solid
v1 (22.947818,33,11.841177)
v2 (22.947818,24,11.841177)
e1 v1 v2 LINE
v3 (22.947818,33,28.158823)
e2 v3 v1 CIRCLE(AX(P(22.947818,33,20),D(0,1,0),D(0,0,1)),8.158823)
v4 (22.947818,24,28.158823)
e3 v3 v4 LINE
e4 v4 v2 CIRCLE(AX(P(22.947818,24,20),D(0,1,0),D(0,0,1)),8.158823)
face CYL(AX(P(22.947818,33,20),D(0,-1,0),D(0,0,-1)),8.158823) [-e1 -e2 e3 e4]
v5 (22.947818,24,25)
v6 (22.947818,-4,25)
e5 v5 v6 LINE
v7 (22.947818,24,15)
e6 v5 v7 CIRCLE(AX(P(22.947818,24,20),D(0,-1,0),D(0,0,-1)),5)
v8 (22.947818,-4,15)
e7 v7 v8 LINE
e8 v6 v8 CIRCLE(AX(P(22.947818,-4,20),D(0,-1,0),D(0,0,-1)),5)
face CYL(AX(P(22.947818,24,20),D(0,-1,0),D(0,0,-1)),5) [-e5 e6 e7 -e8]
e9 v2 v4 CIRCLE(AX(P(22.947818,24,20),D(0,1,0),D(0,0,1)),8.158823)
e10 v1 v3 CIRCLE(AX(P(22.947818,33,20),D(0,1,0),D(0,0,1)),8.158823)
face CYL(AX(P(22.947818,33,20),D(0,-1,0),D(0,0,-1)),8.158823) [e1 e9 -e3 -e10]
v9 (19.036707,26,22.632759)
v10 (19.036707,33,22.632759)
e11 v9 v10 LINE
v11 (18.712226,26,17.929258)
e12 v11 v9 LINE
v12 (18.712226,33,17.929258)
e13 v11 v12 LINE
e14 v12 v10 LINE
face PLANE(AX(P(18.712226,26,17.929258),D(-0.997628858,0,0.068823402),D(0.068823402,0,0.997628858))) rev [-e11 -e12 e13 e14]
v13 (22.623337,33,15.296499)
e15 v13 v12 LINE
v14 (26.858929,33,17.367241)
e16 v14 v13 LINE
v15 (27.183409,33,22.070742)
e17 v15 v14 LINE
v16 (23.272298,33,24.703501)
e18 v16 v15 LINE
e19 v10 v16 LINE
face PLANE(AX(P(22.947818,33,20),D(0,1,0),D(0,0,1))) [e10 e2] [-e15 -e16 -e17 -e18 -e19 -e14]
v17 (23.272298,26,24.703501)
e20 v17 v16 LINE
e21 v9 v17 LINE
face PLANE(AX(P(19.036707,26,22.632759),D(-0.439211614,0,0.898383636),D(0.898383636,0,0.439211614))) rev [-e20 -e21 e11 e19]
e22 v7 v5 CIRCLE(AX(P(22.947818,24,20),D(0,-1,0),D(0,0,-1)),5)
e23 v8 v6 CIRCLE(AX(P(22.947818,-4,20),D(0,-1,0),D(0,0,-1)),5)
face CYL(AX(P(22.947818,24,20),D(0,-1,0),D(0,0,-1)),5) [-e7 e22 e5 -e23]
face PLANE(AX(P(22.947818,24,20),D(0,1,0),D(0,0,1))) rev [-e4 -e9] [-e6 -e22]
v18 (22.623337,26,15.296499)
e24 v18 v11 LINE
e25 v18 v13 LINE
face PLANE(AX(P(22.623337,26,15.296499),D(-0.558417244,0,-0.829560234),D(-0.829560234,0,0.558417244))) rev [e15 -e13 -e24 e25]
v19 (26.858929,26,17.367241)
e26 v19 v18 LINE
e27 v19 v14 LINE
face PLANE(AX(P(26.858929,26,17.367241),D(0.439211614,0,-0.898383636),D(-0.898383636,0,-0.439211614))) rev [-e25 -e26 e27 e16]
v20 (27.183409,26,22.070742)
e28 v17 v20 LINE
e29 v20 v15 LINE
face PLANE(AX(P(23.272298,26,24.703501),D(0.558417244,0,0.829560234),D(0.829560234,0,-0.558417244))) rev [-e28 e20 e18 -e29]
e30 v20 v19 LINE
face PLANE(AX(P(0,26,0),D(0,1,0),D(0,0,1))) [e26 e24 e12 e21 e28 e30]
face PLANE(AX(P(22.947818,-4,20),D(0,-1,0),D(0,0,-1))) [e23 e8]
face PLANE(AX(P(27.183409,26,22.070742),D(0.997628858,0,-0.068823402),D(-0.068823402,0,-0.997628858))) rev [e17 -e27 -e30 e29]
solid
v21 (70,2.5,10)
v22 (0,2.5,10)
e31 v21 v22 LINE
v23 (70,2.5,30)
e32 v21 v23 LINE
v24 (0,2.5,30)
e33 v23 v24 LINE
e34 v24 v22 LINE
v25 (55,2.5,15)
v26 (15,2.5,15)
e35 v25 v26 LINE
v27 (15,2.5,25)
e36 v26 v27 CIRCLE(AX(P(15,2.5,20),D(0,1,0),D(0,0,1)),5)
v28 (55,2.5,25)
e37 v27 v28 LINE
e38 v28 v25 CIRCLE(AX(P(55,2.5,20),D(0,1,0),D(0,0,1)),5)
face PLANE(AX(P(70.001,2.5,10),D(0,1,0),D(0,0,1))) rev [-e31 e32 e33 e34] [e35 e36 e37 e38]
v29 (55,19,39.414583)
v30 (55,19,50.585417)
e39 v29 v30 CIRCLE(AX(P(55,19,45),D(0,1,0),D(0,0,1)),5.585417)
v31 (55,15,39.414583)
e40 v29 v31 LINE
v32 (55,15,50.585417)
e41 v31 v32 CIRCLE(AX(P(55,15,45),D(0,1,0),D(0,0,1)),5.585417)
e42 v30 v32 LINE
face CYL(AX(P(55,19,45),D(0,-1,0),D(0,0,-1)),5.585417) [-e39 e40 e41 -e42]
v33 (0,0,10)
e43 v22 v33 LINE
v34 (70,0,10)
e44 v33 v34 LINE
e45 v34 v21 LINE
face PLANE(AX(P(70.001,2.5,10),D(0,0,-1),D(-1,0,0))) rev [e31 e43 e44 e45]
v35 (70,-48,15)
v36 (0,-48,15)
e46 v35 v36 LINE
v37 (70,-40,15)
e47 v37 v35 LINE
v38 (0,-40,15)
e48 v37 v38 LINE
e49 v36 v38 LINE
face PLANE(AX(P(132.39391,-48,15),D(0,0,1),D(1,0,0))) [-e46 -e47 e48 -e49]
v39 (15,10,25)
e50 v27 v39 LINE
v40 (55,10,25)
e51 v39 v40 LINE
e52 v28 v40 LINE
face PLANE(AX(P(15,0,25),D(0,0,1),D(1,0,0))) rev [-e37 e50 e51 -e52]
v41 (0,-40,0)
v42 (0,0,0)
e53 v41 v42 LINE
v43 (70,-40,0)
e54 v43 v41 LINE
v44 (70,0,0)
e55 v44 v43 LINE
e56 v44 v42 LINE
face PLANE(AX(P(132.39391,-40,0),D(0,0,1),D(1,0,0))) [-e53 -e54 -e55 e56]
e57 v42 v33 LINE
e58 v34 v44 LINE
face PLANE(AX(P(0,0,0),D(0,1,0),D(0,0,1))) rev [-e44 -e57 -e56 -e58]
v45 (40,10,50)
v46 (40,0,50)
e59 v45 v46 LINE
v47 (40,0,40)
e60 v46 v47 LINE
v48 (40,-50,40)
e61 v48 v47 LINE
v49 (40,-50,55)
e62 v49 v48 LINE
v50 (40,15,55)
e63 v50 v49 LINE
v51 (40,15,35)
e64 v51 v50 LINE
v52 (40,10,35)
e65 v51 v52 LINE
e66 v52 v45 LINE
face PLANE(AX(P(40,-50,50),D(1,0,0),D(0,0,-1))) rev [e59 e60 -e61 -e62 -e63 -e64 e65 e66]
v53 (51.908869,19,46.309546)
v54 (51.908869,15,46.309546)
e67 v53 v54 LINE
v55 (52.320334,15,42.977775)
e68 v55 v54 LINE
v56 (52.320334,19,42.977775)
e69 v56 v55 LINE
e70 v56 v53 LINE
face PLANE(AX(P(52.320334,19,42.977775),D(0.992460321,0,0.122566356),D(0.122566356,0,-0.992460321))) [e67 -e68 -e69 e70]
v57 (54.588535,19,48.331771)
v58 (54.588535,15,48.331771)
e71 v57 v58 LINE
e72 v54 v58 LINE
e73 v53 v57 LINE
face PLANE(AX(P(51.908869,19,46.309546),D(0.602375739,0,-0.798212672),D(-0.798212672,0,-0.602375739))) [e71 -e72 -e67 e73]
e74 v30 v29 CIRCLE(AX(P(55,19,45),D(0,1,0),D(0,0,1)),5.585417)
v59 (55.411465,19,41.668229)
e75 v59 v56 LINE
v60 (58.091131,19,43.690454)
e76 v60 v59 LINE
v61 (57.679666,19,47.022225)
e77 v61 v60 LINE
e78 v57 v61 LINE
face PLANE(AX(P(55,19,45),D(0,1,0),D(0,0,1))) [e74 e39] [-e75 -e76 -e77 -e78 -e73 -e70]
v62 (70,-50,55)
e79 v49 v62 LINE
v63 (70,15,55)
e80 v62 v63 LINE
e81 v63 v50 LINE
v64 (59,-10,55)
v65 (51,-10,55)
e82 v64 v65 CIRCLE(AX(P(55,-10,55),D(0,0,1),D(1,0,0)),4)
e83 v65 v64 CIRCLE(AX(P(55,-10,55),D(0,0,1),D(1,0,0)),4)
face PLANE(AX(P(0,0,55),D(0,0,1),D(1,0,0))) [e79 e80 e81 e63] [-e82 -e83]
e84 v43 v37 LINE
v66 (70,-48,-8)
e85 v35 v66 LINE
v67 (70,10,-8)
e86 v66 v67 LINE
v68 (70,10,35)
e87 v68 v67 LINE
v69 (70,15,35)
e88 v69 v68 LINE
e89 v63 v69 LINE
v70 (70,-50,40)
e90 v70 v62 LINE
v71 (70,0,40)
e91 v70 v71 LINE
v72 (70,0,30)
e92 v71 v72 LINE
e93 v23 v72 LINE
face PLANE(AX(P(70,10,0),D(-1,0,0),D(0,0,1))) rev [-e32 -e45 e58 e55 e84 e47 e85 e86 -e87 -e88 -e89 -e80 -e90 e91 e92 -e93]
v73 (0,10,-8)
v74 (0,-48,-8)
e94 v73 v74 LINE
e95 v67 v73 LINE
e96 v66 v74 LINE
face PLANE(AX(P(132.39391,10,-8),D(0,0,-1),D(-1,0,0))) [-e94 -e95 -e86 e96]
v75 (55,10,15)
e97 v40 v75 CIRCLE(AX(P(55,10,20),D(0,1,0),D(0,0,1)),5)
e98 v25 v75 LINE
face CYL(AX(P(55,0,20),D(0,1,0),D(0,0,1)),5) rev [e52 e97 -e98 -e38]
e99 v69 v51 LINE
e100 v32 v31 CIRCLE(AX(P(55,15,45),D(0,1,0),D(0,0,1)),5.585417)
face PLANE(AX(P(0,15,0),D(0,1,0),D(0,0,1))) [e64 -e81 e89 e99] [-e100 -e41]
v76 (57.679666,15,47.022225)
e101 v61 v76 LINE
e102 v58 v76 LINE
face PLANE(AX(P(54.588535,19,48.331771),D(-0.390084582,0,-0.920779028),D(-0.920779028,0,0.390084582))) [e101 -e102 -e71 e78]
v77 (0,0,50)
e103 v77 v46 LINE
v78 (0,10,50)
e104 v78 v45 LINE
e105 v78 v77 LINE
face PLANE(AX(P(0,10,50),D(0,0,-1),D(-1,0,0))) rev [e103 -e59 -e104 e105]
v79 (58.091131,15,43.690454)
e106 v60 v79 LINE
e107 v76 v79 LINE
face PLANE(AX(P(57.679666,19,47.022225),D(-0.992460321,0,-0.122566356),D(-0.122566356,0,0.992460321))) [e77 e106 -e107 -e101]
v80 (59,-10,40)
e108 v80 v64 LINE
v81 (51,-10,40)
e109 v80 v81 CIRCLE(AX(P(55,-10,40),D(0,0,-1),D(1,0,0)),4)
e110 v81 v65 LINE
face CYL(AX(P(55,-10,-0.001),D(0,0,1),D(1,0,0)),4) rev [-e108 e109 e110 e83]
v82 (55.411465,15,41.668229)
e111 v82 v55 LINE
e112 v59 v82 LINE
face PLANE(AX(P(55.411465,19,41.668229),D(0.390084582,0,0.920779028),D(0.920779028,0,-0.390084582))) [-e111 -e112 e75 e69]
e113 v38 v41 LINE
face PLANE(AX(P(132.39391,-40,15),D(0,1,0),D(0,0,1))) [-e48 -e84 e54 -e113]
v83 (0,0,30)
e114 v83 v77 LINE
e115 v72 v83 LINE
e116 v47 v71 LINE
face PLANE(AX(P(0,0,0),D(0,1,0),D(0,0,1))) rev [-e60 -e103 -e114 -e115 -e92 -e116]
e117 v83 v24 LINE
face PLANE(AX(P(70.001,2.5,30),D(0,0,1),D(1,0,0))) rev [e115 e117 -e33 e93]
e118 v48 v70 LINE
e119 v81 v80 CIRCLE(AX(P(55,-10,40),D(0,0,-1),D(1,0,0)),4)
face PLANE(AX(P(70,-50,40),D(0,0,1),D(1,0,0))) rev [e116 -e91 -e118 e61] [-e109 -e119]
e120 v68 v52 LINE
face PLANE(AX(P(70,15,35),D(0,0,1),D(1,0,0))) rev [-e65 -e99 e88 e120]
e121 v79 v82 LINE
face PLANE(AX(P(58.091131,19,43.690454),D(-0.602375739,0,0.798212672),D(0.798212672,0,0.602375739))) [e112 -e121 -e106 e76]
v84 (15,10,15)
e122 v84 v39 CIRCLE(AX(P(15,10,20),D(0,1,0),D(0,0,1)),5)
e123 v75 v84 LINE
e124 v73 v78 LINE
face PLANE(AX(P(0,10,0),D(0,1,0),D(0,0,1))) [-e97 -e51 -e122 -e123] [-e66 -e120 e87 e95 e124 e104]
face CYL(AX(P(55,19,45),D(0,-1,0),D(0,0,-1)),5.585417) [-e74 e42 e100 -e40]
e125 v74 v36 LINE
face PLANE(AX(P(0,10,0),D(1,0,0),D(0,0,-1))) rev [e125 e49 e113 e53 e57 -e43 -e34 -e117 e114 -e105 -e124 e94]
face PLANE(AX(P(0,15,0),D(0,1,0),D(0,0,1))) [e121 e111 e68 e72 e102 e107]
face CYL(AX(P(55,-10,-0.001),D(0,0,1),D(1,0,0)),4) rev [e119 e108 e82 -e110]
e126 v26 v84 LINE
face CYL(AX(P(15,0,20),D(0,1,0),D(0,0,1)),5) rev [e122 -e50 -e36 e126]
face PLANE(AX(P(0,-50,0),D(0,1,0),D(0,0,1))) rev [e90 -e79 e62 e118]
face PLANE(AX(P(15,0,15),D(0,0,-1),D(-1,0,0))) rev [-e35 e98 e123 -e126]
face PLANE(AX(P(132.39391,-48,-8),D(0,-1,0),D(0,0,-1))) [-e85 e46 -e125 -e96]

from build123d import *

# Parameters (mm, degrees)
SKETCH1_W                = 70
SKETCH1_H                = 50
BOSS_EXTRUDE1_DEPTH      = 10
SKETCH2_W                = 30
SKETCH2_H                = 10
BOSS_EXTRUDE2_DEPTH      = 50
SKETCH3_W                = 30
SKETCH3_H                = 15
BOSS_EXTRUDE3_DEPTH      = 5
SKETCH4_W                = 30
SKETCH4_H                = 65
BOSS_EXTRUDE4_DEPTH      = 5
CUT_EXTRUDE1_DEPTH       = 10
CUT_EXTRUDE2_REACH       = 104.103
SKETCH6_W                = 20
SKETCH6_H                = 5
SKETCH7_R                = 5.585417207
BOSS_EXTRUDE5_DEPTH      = 4
CUT_EXTRUDE3_REACH       = 104.103
SKETCH8_R                = 4
BOSS_EXTRUDE6_DEPTH      = 4
BOSS_EXTRUDE6_DEPTH_BACK = 24
SKETCH9_R                = 5
SKETCH10_R               = 8.158822916
BOSS_EXTRUDE7_DEPTH      = 9
CUT_EXTRUDE4_DEPTH       = 7
BOSS_EXTRUDE8_DEPTH      = 70


with BuildPart() as part:
    # Sketch1 → Boss-Extrude1 (new body)
    with BuildSketch(Plane(origin=(0, 0, 0), x_dir=(1, 0, 0), z_dir=(0, 1, 0))):
        with Locations((35, -25)):
            Rectangle(SKETCH1_W, SKETCH1_H)
    extrude(amount=BOSS_EXTRUDE1_DEPTH)

    # Sketch2 → Boss-Extrude2 (add)
    with BuildSketch(Plane.XZ):
        with Locations((55, 45)):
            Rectangle(SKETCH2_W, SKETCH2_H)
    extrude(amount=BOSS_EXTRUDE2_DEPTH)

    # Sketch3 → Boss-Extrude3 (add)
    with BuildSketch(Plane(origin=(0, 10, 0), x_dir=(1, 0, 0), z_dir=(0, 1, 0))):
        with Locations((55, -42.5)):
            Rectangle(SKETCH3_W, SKETCH3_H)
    extrude(amount=BOSS_EXTRUDE3_DEPTH)

    # Sketch4 → Boss-Extrude4 (add)
    with BuildSketch(Plane.XY.offset(50)):
        with Locations((55, -17.5)):
            Rectangle(SKETCH4_W, SKETCH4_H)
    extrude(amount=BOSS_EXTRUDE4_DEPTH)

    # Sketch5 → Cut-Extrude1 (cut)
    with BuildSketch(Plane(origin=(0, 10, 0), x_dir=(1, 0, 0), z_dir=(0, 1, 0))):
        with BuildLine():
            Line((15, -15), (55, -15))
            ThreePointArc((55, -15), (60, -20), (55, -25))
            Line((55, -25), (15, -25))
            ThreePointArc((15, -25), (10, -20), (15, -15))
        make_face()
    extrude(amount=-CUT_EXTRUDE1_DEPTH, mode=Mode.SUBTRACT)

    # Sketch6 → Cut-Extrude2 (cut, up to next)
    with BuildSketch(Plane.ZY, mode=Mode.PRIVATE) as cut_extrude2_sk1:
        with Locations((20, 0)):
            Rectangle(SKETCH6_W, SKETCH6_H)
    cut_extrude2_tool1 = extrude(cut_extrude2_sk1.sketch, amount=-CUT_EXTRUDE2_REACH, mode=Mode.PRIVATE) & part.part
    add(cut_extrude2_tool1.solids().sort_by_distance((0, 0, 20))[0], mode=Mode.SUBTRACT)

    # Sketch7 → Boss-Extrude5 (add)
    with BuildSketch(Plane(origin=(0, 15, 0), x_dir=(1, 0, 0), z_dir=(0, 1, 0))):
        with Locations(Location((55, -45, 0), (0, 0, 270))):
            Circle(SKETCH7_R)
        Polygon((57.67966577, -47.022225035), (58.091131137, -43.690453887), (55.411465367, -41.668228852), (52.32033423, -42.977774965), (51.908868863, -46.309546113), (54.588534633, -48.331771148), align=None, mode=Mode.SUBTRACT)
    extrude(amount=BOSS_EXTRUDE5_DEPTH)

    # Sketch8 → Cut-Extrude3 (cut, up to next)
    with BuildSketch(Plane.XY.offset(55), mode=Mode.PRIVATE) as cut_extrude3_sk1:
        with Locations((55, -10)):
            Circle(SKETCH8_R)
    cut_extrude3_tool1 = extrude(cut_extrude3_sk1.sketch, amount=-CUT_EXTRUDE3_REACH, mode=Mode.PRIVATE) & part.part
    add(cut_extrude3_tool1.solids().sort_by_distance((55, -10, 55))[0], mode=Mode.SUBTRACT)

    # Sketch12 → Boss-Extrude8 (add)
    with BuildSketch(Plane.ZY):
        Polygon((0, 10), (-8, 10), (-8, -48), (15, -48), (15, -40), (0, -40), align=None)
    extrude(amount=-BOSS_EXTRUDE8_DEPTH)


with BuildPart() as body_2:
    # Sketch9 → Boss-Extrude6 (new, two sides: drawn at the far end of the back side and taken through both)
    with BuildSketch(Plane.XZ.offset(-BOSS_EXTRUDE6_DEPTH_BACK)):
        with Locations(Location((22.947817681, 20, 0), (0, 0, 270))):
            Circle(SKETCH9_R)
    extrude(amount=BOSS_EXTRUDE6_DEPTH + BOSS_EXTRUDE6_DEPTH_BACK)

    # Sketch10 → Boss-Extrude7 (add)
    with BuildSketch(Plane(origin=(0, 24, 0), x_dir=(1, 0, 0), z_dir=(0, 1, 0))):
        with Locations(Location((22.947817681, -20, 0), (0, 0, 270))):
            Circle(SKETCH10_R)
    extrude(amount=BOSS_EXTRUDE7_DEPTH)

    # Sketch11 → Cut-Extrude4 (cut)
    with BuildSketch(Plane(origin=(0, 33, 0), x_dir=(1, 0, 0), z_dir=(0, 1, 0))):
        Polygon((27.183408911, -22.07074215), (26.858928603, -17.367241469), (22.623337372, -15.296499319), (18.71222645, -17.92925785), (19.036706759, -22.632758531), (23.272297989, -24.703500681), align=None)
    extrude(amount=-CUT_EXTRUDE4_DEPTH, mode=Mode.SUBTRACT)


solid = Compound([part.part, body_2.part])
